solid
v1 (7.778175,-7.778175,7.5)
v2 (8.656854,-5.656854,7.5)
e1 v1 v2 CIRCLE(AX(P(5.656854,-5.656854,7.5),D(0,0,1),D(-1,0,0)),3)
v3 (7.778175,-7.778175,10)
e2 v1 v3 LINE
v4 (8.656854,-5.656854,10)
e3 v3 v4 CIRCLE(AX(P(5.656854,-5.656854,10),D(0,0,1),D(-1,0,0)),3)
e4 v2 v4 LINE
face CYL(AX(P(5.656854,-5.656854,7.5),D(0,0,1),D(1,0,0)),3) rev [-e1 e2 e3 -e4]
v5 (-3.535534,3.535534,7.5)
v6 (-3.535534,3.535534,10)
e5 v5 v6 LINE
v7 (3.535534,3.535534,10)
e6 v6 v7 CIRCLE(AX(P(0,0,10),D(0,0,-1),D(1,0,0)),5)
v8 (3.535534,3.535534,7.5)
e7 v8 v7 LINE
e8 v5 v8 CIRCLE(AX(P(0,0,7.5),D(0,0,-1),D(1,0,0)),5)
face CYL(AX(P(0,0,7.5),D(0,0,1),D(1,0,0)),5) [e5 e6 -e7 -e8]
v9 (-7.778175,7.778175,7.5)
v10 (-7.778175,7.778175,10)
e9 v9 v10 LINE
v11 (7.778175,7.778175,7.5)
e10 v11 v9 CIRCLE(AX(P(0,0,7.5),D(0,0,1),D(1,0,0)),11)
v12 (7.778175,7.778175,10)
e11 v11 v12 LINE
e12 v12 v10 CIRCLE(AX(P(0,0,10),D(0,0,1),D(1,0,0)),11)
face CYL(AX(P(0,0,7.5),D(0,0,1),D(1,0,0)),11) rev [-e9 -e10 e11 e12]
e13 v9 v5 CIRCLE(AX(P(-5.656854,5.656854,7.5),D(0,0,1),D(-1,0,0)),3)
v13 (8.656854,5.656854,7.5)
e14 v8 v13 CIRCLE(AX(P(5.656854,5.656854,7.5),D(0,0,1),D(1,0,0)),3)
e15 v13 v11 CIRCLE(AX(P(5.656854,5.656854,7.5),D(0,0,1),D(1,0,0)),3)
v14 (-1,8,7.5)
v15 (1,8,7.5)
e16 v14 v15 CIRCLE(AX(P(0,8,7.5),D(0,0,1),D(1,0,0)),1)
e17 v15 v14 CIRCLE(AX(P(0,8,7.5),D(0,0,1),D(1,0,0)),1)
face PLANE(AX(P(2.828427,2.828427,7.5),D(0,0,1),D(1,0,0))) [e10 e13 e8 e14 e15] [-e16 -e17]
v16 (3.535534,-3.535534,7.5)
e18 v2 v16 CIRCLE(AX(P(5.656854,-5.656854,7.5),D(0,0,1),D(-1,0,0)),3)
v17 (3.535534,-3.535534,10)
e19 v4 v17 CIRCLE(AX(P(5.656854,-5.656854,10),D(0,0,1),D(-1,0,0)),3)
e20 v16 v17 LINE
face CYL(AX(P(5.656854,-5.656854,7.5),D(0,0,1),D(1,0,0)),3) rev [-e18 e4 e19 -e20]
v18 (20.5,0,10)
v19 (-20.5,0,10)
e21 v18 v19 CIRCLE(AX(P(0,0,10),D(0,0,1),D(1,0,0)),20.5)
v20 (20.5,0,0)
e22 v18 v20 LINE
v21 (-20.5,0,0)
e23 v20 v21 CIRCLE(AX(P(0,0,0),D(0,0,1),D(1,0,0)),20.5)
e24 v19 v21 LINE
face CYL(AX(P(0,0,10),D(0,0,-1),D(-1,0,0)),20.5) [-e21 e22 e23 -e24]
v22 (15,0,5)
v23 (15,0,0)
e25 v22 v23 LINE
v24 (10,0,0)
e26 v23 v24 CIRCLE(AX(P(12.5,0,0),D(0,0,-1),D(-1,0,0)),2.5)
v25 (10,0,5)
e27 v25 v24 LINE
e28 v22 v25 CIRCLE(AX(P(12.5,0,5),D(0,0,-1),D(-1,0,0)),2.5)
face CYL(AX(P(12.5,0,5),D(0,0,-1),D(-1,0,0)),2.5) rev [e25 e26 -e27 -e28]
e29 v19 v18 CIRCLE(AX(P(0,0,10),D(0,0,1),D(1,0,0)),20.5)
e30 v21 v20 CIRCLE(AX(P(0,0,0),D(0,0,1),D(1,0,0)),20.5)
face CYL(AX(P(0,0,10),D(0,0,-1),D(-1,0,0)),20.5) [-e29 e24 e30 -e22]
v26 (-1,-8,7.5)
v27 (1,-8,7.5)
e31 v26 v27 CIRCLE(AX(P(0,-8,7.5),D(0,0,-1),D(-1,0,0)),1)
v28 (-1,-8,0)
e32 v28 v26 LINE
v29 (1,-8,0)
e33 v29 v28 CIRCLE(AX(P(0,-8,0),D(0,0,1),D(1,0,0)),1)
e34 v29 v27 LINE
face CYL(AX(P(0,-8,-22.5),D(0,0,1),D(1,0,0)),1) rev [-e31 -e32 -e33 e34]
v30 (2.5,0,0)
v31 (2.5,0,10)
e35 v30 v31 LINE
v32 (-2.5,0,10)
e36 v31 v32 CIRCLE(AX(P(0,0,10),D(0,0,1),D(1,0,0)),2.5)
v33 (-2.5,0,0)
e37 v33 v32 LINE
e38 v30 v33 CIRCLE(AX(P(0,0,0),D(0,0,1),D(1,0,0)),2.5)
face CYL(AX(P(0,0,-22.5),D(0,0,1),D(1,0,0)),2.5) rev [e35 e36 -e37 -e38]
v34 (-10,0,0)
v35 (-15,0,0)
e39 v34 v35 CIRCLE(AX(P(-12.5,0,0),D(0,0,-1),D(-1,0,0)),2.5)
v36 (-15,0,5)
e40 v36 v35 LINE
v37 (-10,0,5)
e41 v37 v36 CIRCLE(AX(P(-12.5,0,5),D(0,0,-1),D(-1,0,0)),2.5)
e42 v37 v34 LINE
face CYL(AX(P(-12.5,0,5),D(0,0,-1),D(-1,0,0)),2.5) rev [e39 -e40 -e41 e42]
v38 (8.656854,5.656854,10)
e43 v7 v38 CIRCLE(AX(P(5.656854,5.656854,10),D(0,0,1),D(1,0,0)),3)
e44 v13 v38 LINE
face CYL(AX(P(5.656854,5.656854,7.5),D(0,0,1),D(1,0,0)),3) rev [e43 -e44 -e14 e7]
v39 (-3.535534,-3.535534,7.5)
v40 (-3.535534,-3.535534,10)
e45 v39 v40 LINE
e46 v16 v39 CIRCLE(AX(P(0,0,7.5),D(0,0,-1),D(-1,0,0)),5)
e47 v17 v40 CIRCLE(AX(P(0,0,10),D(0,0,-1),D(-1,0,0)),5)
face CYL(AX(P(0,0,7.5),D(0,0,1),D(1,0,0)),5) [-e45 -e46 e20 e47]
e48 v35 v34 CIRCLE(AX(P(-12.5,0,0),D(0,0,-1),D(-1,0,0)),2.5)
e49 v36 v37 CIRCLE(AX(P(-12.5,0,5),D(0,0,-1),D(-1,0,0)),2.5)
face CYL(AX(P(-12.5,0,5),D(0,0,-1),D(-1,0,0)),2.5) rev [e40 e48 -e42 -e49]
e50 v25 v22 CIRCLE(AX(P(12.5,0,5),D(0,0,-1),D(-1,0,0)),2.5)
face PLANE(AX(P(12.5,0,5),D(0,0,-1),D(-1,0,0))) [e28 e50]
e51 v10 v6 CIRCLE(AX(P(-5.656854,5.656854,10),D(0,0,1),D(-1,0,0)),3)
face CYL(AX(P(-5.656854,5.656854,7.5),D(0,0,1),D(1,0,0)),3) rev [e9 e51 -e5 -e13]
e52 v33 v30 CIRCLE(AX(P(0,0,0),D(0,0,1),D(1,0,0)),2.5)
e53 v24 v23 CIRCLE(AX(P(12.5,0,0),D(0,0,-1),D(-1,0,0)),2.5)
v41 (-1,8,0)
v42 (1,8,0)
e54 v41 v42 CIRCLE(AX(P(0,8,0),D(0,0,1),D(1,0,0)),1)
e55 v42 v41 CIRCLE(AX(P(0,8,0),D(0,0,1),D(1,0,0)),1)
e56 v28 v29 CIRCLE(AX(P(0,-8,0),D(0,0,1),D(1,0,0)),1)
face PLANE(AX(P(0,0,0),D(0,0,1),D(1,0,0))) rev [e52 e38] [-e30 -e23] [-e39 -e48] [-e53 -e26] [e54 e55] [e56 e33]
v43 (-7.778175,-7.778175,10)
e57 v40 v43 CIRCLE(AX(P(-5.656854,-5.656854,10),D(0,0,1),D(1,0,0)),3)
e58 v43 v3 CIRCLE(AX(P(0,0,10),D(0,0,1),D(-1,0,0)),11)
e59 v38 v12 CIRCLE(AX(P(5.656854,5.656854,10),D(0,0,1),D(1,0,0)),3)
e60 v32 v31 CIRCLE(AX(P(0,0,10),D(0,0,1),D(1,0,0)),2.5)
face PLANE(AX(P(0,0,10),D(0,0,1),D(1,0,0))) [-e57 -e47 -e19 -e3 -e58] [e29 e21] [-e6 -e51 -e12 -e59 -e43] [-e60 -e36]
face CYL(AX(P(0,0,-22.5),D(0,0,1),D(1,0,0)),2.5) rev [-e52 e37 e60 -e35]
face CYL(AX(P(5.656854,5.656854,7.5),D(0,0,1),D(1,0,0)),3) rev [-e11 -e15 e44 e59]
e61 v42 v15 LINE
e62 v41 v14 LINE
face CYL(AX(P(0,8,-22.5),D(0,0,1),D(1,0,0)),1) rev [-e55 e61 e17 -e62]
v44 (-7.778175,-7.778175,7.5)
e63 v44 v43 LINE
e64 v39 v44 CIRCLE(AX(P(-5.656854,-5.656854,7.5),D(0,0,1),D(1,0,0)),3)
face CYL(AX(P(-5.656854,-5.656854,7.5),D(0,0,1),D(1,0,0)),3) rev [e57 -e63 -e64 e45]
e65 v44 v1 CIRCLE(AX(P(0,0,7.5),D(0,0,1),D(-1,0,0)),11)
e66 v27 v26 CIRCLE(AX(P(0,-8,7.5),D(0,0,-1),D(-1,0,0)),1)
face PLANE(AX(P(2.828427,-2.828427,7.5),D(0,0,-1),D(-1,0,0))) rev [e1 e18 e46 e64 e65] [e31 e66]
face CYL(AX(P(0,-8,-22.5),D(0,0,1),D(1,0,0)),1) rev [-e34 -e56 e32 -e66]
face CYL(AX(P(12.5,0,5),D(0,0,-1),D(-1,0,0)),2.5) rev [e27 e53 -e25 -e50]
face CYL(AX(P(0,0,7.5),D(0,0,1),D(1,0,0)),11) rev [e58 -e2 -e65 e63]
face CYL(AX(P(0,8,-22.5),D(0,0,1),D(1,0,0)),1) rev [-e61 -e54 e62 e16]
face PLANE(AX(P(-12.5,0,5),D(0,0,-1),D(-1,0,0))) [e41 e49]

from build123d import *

# Parameters (mm, degrees)
DISC_PROFILE_41_R         = 20.5
PORT_BLOCK_DISC_DEPTH     = 10
ARC_PORT_SLOTS_DEPTH      = 2.5
THROUGH_PORTS_PROFILE_R   = 2.5
THROUGH_PORTS_PROFILE_R_2 = 1
THROUGH_PORTS_DEPTH       = 32.5
PORT_POCKETS_PROFILE_R    = 2.5
PORT_POCKETS_DEPTH        = 5


with BuildPart() as part:
    # Disc Profile Ø41 → Port Block Disc (new body)
    with BuildSketch(Plane.XY):
        Circle(DISC_PROFILE_41_R)
    extrude(amount=PORT_BLOCK_DISC_DEPTH)

    # Arc Port Slots Profile → Arc Port Slots (cut)
    with BuildSketch(Plane.XY.offset(10)):
        with BuildLine():
            ThreePointArc((7.778174593, 7.778174593), (0, 11), (-7.778174593, 7.778174593))
            ThreePointArc((-7.778174593, 7.778174593), (-7.778174593, 3.535533906), (-3.535533906, 3.535533906))
            ThreePointArc((-3.535533906, 3.535533906), (0, 5), (3.535533906, 3.535533906))
            ThreePointArc((3.535533906, 3.535533906), (7.778174593, 3.535533906), (7.778174593, 7.778174593))
        make_face()
        with BuildLine():
            ThreePointArc((3.535533906, -3.535533906), (0, -5), (-3.535533906, -3.535533906))
            ThreePointArc((-3.535533906, -3.535533906), (-7.778174593, -3.535533906), (-7.778174593, -7.778174593))
            ThreePointArc((-7.778174593, -7.778174593), (0, -11), (7.778174593, -7.778174593))
            ThreePointArc((7.778174593, -7.778174593), (7.778174593, -3.535533906), (3.535533906, -3.535533906))
        make_face()
    extrude(amount=-ARC_PORT_SLOTS_DEPTH, mode=Mode.SUBTRACT)

    # Through Ports Profile → Through Ports (cut)
    with BuildSketch(Plane.XY.offset(10)):
        Circle(THROUGH_PORTS_PROFILE_R)
        with Locations((0, 8)):
            Circle(THROUGH_PORTS_PROFILE_R_2)
        with Locations((0, -8)):
            Circle(THROUGH_PORTS_PROFILE_R_2)
    extrude(amount=-THROUGH_PORTS_DEPTH, mode=Mode.SUBTRACT)

    # Port Pockets Profile → Port Pockets (cut)
    with BuildSketch(Plane(origin=(0, 0, 0), x_dir=(-1, 0, 0), z_dir=(0, 0, -1))):
        with Locations((12.5, 0)):
            Circle(PORT_POCKETS_PROFILE_R)
        with Locations((-12.5, 0)):
            Circle(PORT_POCKETS_PROFILE_R)
    extrude(amount=-PORT_POCKETS_DEPTH, mode=Mode.SUBTRACT)


solid = part.part
